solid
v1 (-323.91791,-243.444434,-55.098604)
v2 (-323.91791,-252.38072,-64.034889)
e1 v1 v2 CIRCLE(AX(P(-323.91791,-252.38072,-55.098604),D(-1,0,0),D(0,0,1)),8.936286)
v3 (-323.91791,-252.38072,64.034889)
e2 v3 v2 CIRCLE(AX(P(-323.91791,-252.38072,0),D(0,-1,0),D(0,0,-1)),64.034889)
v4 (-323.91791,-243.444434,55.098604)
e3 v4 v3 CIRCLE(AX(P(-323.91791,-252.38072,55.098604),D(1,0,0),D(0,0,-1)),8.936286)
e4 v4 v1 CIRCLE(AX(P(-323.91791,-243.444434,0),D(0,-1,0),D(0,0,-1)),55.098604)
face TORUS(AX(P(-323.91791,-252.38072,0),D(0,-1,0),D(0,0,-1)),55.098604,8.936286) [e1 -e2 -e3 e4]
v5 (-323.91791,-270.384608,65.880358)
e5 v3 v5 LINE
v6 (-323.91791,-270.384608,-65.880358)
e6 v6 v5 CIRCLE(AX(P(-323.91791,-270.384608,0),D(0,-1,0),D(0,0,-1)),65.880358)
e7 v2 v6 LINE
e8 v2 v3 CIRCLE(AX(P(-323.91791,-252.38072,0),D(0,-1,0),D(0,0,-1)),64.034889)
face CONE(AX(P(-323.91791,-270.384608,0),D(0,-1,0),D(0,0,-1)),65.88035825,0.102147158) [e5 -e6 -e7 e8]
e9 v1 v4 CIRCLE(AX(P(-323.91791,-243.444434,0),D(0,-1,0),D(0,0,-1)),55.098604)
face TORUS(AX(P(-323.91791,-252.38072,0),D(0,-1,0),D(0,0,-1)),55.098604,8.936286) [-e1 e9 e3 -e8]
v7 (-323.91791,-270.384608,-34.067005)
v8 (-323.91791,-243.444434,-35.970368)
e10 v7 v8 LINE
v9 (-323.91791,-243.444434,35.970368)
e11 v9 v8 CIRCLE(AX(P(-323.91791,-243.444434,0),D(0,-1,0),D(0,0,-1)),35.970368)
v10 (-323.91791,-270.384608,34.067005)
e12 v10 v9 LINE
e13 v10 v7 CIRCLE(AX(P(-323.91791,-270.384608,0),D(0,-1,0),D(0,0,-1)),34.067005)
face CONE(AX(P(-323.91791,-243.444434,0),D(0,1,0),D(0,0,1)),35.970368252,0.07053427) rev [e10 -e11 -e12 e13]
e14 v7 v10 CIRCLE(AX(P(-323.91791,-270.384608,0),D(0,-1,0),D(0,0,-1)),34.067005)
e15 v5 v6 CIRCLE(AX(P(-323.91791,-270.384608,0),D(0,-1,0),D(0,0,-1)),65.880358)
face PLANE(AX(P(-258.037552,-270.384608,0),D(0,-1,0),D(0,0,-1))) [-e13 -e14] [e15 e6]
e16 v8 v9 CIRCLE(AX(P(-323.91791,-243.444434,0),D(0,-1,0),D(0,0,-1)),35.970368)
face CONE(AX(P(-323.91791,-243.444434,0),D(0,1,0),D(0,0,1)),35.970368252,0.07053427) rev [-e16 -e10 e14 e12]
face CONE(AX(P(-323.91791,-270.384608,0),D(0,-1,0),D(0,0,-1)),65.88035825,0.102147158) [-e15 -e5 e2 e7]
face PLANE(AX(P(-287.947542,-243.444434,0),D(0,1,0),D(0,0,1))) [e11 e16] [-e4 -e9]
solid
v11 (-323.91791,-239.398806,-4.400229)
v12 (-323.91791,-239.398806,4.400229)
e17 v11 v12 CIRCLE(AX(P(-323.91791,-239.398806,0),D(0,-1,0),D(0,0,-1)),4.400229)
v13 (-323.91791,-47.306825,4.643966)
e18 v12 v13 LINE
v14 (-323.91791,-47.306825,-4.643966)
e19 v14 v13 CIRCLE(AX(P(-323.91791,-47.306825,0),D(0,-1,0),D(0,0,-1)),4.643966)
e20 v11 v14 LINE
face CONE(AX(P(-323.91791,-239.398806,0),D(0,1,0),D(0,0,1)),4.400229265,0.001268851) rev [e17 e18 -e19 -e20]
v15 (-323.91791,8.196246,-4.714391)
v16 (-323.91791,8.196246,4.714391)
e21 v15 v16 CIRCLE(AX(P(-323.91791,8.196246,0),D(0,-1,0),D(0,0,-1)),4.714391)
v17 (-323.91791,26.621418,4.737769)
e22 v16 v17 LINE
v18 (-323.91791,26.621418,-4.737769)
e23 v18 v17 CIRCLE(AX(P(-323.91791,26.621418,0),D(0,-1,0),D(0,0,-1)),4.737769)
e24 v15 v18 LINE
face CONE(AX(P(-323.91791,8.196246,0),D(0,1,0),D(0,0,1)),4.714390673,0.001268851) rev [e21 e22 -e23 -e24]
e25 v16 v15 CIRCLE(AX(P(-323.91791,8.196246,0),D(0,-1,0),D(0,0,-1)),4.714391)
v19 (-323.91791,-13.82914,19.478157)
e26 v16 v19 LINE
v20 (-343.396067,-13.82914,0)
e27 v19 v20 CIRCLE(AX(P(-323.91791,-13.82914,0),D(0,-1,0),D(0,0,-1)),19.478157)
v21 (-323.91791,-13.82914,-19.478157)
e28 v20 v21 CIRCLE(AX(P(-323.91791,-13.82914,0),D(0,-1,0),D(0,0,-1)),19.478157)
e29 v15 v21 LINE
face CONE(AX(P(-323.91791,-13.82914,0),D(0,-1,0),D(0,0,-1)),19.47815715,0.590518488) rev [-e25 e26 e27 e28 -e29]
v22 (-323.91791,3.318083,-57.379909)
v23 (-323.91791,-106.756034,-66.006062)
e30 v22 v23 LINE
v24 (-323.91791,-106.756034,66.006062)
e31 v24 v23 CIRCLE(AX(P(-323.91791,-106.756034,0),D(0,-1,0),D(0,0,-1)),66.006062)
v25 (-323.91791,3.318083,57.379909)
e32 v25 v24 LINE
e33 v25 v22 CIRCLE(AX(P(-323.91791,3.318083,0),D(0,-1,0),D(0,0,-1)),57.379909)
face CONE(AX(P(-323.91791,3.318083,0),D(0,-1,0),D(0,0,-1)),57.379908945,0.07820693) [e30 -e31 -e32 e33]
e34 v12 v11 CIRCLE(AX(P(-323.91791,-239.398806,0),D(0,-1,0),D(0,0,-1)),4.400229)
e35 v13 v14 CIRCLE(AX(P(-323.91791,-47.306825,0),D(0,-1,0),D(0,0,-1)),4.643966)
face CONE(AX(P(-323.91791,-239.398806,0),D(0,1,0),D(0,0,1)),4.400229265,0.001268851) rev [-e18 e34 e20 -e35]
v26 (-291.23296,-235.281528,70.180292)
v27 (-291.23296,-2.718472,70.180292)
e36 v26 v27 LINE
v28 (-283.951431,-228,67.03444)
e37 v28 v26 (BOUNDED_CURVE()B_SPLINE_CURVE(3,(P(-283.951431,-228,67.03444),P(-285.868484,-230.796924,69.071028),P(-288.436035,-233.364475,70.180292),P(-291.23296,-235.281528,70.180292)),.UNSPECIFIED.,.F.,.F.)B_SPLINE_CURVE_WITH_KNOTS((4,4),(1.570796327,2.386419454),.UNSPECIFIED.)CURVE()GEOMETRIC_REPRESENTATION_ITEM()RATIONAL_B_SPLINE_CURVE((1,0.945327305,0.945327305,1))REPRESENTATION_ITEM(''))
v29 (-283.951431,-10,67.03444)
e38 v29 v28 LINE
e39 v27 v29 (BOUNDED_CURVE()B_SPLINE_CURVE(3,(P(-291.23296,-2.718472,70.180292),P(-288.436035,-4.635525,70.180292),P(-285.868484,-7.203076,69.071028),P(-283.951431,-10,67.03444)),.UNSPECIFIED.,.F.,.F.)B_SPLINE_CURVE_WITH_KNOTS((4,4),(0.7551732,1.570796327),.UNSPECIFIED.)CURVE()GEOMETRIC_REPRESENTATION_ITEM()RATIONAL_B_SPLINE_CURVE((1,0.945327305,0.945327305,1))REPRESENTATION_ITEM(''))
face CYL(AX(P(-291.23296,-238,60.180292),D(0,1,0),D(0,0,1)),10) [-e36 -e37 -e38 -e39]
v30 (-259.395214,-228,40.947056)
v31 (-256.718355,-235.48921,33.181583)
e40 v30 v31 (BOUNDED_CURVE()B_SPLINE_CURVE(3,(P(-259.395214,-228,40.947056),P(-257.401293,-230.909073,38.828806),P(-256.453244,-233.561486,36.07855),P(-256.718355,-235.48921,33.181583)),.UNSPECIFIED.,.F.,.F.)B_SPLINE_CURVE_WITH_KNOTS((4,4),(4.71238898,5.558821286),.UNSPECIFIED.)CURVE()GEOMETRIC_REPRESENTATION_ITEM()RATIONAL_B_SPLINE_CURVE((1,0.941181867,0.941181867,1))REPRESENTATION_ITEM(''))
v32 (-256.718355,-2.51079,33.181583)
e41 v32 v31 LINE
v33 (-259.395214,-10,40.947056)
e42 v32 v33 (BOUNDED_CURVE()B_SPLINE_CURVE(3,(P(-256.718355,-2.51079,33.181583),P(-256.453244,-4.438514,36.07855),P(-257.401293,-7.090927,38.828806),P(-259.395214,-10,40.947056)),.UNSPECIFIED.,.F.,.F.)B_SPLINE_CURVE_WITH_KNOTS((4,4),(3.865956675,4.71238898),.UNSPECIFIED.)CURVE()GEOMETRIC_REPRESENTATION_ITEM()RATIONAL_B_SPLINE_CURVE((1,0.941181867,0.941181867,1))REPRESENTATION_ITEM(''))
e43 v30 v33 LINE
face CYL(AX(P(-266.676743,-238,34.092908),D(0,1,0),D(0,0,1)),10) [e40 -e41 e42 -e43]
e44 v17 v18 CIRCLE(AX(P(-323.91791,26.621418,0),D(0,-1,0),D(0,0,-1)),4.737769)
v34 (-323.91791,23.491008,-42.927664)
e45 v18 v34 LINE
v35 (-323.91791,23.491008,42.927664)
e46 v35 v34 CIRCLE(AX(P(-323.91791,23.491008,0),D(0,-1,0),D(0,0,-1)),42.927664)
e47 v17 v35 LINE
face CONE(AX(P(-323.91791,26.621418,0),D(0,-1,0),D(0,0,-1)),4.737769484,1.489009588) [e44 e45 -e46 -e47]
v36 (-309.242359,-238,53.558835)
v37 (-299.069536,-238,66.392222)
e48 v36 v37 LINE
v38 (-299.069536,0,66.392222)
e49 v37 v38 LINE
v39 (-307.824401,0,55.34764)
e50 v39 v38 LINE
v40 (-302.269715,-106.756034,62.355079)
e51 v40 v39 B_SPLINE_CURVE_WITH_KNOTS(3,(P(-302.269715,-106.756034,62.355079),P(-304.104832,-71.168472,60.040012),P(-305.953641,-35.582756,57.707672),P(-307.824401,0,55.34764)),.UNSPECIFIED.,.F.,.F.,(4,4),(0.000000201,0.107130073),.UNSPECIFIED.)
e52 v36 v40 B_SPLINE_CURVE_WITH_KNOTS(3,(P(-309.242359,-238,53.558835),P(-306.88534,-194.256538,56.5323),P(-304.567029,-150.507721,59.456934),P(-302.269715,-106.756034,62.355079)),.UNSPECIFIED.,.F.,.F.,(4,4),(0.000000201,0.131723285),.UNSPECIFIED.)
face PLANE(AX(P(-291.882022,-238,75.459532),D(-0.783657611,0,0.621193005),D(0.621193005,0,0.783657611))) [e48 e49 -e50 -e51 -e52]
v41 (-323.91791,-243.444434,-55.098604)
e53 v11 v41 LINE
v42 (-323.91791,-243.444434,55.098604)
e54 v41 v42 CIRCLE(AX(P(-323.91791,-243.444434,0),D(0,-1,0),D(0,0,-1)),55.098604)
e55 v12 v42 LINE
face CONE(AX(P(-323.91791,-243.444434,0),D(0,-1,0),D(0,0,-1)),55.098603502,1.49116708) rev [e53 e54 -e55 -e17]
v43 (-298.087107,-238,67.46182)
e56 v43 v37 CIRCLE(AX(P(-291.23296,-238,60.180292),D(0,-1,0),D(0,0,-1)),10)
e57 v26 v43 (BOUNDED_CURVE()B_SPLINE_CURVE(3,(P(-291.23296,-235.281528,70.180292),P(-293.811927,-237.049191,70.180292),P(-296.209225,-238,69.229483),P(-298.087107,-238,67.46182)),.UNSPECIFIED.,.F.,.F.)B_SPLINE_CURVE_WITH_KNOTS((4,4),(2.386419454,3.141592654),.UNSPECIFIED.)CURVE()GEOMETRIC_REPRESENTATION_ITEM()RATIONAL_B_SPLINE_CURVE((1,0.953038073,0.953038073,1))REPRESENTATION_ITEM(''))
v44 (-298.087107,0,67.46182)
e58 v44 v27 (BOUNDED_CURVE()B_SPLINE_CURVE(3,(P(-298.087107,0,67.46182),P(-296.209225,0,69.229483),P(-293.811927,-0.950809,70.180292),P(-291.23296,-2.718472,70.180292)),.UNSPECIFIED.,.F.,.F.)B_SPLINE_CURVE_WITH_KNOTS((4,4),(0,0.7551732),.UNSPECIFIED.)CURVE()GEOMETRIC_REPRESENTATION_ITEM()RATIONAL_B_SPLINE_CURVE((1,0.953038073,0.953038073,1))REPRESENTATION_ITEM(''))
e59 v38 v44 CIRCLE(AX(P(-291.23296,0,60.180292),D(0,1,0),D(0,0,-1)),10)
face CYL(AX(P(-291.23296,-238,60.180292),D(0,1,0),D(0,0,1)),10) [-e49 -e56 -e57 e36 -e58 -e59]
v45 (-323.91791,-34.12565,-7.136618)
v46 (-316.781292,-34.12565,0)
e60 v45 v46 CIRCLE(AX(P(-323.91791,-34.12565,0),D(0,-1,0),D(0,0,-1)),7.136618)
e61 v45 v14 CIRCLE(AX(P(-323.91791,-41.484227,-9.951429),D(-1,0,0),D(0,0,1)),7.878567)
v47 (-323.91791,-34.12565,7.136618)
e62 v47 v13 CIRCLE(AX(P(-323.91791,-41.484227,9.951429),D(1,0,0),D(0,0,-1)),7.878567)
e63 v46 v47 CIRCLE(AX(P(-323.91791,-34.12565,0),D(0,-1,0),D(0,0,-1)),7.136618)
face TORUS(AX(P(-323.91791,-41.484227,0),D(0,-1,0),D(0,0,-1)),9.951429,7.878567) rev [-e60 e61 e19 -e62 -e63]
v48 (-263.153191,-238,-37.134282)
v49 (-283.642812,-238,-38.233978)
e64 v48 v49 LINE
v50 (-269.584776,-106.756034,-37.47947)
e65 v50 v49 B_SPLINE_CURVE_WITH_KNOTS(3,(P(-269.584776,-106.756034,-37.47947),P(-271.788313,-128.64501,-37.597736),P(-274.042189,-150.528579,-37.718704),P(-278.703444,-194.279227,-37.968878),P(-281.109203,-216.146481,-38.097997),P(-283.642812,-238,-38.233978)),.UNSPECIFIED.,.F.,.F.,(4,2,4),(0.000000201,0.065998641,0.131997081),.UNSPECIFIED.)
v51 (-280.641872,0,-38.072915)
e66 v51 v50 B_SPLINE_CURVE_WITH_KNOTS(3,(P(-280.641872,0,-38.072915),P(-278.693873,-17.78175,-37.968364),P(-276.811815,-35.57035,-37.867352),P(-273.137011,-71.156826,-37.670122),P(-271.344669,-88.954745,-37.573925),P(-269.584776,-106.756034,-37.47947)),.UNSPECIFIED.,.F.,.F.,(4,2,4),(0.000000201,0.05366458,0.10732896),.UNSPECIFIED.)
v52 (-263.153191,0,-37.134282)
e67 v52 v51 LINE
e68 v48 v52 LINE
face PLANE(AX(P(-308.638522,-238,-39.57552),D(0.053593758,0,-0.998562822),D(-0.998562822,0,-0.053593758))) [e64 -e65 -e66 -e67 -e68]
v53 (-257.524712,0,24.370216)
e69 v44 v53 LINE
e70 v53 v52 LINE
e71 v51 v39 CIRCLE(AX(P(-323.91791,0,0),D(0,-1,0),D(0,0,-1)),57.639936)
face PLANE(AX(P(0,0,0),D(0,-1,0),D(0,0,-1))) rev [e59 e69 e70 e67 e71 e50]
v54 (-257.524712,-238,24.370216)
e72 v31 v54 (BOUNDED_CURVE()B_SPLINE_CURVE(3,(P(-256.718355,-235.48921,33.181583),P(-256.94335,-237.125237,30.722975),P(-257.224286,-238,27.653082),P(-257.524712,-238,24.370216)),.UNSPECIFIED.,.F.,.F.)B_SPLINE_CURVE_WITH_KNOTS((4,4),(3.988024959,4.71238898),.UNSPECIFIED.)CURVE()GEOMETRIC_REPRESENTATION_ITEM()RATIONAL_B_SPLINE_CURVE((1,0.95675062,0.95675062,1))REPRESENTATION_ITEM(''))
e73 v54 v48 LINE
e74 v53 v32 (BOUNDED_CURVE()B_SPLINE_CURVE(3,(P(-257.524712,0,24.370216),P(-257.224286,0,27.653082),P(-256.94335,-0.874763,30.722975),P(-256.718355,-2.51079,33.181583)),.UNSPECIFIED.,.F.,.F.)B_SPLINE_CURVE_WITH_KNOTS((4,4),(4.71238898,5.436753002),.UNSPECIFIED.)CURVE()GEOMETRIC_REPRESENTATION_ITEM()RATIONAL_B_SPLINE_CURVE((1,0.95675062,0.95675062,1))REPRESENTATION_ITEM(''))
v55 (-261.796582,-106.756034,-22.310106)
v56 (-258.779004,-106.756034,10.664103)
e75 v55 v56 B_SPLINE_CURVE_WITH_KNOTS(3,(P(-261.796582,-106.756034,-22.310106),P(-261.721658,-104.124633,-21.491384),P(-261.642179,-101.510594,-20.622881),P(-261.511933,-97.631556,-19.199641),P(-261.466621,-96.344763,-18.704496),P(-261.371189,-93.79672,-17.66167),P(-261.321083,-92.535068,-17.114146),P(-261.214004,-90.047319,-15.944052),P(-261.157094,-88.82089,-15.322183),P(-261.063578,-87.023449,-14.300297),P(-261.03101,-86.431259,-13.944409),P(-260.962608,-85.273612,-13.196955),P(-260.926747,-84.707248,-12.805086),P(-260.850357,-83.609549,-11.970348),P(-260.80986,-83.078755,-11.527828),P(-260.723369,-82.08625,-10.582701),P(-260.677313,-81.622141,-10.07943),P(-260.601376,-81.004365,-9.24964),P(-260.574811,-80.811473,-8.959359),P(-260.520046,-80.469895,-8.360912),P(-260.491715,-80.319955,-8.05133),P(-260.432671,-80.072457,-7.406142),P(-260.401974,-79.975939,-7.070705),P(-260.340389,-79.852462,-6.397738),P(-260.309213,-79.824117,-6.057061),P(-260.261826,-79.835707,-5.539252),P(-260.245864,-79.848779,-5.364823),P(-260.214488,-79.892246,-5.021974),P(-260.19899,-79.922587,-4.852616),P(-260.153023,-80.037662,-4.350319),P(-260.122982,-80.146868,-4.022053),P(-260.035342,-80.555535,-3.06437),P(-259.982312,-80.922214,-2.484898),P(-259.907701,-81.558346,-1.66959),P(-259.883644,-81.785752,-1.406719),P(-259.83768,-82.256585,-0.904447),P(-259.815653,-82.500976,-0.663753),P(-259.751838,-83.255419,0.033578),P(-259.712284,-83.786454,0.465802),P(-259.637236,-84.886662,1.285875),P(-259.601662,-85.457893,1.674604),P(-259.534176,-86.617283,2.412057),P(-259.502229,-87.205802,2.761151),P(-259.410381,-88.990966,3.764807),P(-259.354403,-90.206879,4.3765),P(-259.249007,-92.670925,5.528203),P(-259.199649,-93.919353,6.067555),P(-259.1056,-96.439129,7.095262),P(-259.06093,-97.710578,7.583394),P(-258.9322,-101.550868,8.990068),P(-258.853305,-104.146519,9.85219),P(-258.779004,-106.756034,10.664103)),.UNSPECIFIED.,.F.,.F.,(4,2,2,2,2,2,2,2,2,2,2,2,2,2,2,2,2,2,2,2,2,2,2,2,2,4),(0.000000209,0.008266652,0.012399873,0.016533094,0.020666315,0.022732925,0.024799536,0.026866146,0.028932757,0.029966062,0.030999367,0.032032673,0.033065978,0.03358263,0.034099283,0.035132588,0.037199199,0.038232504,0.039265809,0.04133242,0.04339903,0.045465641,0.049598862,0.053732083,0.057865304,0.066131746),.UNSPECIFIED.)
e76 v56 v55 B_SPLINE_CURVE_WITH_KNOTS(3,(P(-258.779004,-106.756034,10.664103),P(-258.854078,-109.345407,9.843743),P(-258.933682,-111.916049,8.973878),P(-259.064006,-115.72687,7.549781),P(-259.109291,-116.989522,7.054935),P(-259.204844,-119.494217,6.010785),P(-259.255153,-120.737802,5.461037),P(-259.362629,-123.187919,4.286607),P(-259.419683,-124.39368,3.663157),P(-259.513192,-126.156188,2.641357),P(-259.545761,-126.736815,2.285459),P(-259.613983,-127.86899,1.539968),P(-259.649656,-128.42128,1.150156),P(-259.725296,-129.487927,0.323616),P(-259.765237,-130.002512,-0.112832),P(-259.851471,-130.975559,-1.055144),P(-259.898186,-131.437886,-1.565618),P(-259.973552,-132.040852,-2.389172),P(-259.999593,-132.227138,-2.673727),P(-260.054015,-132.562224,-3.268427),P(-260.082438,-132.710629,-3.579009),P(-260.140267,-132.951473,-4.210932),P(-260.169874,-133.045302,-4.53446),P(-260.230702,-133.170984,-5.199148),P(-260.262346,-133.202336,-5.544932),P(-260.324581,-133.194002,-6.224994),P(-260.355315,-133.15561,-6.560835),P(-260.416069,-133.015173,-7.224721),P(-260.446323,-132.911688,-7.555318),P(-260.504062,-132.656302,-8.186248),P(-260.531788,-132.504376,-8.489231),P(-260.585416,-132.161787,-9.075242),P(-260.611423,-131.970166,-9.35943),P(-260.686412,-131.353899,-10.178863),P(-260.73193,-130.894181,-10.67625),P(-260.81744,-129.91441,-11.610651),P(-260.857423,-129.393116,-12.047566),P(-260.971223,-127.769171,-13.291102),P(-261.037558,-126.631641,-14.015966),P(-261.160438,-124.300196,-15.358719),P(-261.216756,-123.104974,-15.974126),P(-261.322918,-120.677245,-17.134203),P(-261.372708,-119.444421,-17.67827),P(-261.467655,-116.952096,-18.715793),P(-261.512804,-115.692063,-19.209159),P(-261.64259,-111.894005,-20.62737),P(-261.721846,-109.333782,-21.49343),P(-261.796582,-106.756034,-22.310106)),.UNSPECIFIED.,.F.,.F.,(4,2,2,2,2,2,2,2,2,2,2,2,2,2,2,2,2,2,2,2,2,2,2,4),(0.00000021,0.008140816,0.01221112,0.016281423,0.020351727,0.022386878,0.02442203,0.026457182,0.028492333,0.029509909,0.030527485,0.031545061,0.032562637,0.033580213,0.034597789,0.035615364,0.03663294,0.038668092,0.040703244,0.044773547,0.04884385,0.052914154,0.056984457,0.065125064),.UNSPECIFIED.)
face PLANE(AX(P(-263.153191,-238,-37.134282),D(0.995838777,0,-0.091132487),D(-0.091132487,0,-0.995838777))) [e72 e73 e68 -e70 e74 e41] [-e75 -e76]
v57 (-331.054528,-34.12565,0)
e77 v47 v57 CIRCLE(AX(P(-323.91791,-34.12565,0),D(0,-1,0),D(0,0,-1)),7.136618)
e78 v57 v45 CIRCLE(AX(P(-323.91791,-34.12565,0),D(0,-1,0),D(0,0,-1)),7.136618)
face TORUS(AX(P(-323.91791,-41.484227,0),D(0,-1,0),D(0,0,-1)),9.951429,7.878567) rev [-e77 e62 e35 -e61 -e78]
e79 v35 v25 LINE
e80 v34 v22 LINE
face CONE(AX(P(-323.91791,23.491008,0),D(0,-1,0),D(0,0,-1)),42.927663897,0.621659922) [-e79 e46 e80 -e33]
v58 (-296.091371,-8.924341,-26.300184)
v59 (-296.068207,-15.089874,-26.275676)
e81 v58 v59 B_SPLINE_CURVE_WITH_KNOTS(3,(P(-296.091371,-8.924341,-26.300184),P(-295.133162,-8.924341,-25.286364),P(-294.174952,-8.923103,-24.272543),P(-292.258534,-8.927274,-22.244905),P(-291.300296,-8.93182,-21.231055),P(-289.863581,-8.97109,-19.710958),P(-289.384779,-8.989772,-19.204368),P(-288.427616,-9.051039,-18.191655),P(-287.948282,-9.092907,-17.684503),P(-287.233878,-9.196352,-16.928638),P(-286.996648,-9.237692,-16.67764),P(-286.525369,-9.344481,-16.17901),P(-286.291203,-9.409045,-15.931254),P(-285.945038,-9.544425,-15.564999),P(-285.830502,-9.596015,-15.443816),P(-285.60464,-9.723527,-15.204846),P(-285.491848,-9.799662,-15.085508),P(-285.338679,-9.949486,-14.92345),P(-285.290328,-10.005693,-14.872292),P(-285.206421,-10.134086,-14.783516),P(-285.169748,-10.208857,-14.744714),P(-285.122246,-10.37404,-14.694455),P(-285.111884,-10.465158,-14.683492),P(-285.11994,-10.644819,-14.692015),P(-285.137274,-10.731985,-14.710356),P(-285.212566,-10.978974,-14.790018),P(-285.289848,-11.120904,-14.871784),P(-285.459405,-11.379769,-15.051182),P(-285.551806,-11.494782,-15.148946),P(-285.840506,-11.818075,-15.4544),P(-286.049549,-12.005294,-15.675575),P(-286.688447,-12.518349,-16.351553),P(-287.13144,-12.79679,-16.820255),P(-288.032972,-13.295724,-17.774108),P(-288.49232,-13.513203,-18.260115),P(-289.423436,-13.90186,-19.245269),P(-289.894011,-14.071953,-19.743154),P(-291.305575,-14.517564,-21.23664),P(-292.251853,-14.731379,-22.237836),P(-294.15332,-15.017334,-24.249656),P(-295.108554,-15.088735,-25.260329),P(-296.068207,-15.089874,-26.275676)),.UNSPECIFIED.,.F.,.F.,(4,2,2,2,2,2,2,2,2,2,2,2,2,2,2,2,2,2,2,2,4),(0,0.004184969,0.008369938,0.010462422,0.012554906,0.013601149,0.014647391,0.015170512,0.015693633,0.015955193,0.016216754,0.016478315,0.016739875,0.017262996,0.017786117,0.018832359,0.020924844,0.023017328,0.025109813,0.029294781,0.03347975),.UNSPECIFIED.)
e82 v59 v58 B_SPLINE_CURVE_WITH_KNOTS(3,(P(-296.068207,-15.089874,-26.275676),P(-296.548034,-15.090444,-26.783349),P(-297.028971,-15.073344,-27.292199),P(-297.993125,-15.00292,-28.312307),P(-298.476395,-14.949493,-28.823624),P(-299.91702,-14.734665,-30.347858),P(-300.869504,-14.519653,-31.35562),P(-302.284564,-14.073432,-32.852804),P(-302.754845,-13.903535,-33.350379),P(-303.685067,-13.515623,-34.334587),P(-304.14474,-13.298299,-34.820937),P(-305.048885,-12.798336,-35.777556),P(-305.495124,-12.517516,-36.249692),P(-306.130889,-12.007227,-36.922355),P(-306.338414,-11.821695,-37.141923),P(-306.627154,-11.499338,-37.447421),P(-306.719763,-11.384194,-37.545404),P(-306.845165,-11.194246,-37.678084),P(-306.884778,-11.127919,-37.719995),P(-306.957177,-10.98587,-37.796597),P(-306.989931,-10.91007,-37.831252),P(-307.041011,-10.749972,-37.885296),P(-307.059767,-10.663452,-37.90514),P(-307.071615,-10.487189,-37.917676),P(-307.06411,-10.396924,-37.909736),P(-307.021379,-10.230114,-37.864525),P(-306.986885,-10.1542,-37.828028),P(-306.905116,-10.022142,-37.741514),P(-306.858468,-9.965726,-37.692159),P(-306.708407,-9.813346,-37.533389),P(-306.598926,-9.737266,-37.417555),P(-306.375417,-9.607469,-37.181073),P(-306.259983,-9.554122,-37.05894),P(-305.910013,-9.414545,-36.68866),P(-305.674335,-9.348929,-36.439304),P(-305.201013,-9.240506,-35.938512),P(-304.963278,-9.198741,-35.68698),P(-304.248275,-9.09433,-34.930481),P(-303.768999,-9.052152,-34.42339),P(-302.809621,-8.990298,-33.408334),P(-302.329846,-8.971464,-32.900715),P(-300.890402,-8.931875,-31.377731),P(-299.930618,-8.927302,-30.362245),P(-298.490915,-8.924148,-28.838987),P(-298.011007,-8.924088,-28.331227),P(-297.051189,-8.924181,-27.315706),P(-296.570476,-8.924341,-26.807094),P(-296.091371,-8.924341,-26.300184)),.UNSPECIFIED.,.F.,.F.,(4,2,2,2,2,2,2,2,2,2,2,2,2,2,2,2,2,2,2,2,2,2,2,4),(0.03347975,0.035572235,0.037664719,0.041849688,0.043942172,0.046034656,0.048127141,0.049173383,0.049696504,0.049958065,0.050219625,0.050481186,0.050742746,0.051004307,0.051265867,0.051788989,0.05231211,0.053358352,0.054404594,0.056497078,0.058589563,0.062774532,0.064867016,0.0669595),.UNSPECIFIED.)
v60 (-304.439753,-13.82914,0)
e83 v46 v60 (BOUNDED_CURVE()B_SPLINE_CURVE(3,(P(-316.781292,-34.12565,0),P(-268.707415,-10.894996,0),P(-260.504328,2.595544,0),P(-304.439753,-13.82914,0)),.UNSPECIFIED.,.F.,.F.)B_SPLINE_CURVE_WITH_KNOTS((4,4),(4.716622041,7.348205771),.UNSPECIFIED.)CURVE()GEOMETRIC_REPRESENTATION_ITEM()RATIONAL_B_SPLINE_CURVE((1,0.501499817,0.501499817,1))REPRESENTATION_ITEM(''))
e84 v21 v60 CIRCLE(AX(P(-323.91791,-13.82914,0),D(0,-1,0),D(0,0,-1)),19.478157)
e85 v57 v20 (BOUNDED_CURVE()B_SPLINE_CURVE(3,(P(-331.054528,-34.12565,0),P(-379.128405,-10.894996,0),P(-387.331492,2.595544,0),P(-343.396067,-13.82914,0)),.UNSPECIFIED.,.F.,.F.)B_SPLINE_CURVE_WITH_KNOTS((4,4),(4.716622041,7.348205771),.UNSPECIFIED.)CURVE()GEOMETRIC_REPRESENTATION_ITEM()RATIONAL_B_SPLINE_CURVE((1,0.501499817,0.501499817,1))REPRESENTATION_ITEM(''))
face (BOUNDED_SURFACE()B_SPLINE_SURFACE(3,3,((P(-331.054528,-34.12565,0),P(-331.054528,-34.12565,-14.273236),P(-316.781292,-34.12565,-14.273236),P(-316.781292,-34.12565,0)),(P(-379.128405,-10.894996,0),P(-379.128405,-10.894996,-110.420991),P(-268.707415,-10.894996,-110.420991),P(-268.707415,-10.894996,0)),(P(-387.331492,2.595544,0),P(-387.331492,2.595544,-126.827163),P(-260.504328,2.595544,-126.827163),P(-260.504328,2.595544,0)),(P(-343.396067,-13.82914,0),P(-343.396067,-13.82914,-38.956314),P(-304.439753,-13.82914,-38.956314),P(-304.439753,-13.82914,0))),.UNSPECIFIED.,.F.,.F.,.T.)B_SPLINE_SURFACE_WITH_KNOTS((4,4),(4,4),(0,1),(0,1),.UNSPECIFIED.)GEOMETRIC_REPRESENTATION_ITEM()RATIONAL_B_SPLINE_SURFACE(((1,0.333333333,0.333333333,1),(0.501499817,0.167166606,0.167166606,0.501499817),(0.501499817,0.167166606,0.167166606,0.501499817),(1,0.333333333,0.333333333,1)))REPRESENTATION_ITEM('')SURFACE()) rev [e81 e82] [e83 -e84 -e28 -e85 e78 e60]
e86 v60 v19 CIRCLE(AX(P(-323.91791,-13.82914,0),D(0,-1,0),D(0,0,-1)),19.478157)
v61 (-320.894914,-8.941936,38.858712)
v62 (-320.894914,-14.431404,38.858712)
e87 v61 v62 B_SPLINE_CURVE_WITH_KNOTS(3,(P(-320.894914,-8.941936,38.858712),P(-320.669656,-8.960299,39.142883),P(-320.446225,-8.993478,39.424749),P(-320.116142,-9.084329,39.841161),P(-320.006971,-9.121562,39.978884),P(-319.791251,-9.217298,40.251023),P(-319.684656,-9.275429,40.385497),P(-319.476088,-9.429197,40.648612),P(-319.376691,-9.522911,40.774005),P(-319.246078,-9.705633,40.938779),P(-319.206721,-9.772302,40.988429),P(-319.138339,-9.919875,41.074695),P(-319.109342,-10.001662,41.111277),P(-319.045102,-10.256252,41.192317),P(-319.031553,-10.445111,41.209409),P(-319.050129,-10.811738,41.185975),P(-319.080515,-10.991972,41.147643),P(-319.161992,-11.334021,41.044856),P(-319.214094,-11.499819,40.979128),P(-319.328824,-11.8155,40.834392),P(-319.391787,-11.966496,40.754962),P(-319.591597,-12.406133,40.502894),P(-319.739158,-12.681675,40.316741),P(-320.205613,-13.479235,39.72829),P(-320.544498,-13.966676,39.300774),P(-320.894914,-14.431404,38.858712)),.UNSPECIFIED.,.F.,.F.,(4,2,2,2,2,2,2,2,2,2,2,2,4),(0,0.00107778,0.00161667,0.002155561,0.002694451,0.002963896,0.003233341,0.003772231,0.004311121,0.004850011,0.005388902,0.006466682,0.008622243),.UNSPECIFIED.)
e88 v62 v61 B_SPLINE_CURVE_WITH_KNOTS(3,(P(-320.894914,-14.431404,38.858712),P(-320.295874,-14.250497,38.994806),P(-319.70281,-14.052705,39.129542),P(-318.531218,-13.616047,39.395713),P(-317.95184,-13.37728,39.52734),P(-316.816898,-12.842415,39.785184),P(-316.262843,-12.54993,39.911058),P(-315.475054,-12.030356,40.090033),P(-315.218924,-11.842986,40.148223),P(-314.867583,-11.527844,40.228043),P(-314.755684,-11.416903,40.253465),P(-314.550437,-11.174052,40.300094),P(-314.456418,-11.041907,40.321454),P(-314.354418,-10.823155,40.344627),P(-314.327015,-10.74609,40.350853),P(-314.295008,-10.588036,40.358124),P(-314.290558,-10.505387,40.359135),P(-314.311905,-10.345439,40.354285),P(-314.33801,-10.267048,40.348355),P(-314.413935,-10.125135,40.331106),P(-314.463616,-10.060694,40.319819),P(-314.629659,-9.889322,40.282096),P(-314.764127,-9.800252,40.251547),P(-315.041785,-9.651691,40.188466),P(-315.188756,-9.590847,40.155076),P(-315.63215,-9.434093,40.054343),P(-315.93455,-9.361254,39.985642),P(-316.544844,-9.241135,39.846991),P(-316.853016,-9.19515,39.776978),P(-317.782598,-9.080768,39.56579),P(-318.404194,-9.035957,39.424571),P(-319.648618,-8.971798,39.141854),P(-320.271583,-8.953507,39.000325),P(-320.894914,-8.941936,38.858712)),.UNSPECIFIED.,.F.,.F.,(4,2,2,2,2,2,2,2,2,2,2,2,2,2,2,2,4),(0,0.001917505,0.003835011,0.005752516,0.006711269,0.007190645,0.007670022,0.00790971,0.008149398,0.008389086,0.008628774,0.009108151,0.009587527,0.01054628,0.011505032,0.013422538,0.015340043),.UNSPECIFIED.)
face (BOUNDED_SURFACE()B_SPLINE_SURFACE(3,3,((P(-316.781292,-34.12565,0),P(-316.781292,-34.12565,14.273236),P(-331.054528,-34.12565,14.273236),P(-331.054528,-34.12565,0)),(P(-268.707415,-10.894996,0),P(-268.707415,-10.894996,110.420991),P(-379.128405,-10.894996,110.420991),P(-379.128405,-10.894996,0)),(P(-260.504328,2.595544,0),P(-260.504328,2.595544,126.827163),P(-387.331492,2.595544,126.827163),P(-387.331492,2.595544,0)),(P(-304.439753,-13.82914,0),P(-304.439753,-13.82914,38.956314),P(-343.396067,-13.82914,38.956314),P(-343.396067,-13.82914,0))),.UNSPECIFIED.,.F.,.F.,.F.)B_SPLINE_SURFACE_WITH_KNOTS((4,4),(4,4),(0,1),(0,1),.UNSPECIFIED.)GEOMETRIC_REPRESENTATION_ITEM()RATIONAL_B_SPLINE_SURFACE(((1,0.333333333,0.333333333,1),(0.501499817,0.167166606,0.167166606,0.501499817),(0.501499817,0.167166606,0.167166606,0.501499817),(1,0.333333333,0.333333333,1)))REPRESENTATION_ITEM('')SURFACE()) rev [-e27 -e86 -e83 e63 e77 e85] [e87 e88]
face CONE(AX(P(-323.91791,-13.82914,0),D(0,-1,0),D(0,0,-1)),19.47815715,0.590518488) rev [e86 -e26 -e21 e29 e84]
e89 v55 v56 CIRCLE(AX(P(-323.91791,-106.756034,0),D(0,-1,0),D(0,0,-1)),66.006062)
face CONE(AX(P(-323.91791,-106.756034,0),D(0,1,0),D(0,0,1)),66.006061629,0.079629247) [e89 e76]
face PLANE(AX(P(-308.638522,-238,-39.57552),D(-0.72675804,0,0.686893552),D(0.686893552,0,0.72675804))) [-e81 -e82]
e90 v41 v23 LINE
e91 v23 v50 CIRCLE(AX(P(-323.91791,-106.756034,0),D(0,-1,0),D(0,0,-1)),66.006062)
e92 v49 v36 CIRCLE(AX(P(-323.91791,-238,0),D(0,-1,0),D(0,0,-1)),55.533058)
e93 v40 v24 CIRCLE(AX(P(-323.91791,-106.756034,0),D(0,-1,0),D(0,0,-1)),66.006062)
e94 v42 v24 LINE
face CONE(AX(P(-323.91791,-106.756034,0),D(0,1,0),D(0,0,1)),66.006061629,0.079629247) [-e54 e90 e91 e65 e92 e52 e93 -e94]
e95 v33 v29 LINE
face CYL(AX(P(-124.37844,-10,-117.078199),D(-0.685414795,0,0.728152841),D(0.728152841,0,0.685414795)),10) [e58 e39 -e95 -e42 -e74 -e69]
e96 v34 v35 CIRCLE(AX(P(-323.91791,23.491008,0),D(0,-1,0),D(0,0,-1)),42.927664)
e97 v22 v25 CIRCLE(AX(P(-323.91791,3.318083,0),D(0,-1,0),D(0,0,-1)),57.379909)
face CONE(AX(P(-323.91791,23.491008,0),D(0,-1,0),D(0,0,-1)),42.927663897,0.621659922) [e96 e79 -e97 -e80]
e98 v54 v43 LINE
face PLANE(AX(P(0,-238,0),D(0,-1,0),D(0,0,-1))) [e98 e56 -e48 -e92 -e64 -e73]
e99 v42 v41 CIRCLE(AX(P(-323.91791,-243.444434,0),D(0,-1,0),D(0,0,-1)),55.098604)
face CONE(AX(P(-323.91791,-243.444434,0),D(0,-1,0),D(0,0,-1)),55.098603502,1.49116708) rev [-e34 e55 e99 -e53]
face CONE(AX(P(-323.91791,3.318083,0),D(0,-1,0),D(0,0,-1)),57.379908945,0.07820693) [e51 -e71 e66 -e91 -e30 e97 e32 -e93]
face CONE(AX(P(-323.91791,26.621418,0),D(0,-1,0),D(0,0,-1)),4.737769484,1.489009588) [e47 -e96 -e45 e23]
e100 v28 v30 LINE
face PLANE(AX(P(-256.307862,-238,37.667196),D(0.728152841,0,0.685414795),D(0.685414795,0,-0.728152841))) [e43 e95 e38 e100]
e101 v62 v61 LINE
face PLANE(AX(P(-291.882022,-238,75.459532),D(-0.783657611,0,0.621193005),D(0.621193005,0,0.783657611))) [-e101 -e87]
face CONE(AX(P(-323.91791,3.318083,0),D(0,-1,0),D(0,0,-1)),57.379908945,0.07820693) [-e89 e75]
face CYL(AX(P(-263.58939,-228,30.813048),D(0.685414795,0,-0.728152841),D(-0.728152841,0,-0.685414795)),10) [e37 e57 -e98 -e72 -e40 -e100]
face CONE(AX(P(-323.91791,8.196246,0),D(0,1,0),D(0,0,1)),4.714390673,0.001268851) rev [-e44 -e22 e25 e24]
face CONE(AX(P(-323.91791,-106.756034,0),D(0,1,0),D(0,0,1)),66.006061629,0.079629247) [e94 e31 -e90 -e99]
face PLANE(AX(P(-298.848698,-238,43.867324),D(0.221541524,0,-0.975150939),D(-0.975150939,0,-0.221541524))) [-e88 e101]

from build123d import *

# Parameters (mm, degrees)
BOSS_EXTRUDE1_DEPTH = 238
FILLET1_R           = 10


with BuildPart() as part:
    # Sketch2 → Revolve1 (revolve)
    with BuildSketch(Plane.XY, mode=Mode.PRIVATE) as revolve1_sk:
        with BuildLine():
            Line((-328.655679382, 26.621417908), (-366.845573795, 23.491008025))
            Line((-366.845573795, 23.491008025), (-381.297818843, 3.318082644))
            Line((-381.297818843, 3.318082644), (-389.923971527, -106.756034051))
            Line((-389.923971527, -106.756034051), (-379.0165134, -243.444434045))
            Line((-379.0165134, -243.444434045), (-328.318139163, -239.398806221))
            Line((-328.318139163, -239.398806221), (-328.561875404, -47.306824662))
            ThreePointArc((-328.561875404, -47.306824662), (-341.610700787, -42.948172925), (-331.054528121, -34.125650186))
            add(Edge.make_bspline(
                [(-343.396067048, -13.829139561), (-369.788894566, -3.962526401), (-364.86114786, -12.066545193), (-359.933401153, -20.170563985), (-331.054528121, -34.125650186)],
                knots=[2.07657219, 2.07657219, 2.07657219, 3.392364055, 3.392364055, 4.70815592, 4.70815592, 4.70815592], degree=2, weights=[1, 0.791280521, 1, 0.791280521, 1]))
            Line((-343.396067048, -13.829139561), (-328.632300571, 8.196246))
            Line((-328.632300571, 8.196246), (-328.655679382, 26.621417908))
        make_face()
    revolve(revolve1_sk.sketch.rotate(Axis((-323.917909898, -239.047676817, 0), (0, 1, 0)), 270), axis=Axis((-323.917909898, -239.047676817, 0), (0, 1, 0)))

    # Sketch3 → Boss-Extrude1 (add)
    with BuildSketch(Plane(origin=(0, 0, 0), x_dir=(1, 0, 0), z_dir=(0, 1, 0))):
        Polygon((-308.638521792, 39.575519818), (-263.153191414, 37.134281554), (-256.30786178, -37.667195745), (-291.882022487, -75.459531675), (-320.894913791, -38.858712112), (-298.848697668, -43.867323718), (-278.655979488, -19.734201659), (-273.594686567, 2.497883967), align=None)
    extrude(amount=-BOSS_EXTRUDE1_DEPTH)

    # Fillet1
    fillet1_edges = [part.edges().sort_by_distance(p)[0] for p in [
        (-291.882022487, -119, 75.459531675),
        (-274.094942134, -238, 56.56336371),
        (-256.30786178, -119, 37.667195745),
        (-274.094942134, 0, 56.56336371),
    ]]
    fillet(fillet1_edges, radius=FILLET1_R)


with BuildPart() as body_2:
    # Sketch5 → Revolve2 (revolve)
    with BuildSketch(Plane.XY, mode=Mode.PRIVATE) as revolve2_sk:
        with BuildLine():
            Line((-287.947541646, -243.444434045), (-268.819306396, -243.444434045))
            ThreePointArc((-268.819306396, -243.444434045), (-262.500398164, -246.061811534), (-259.883020675, -252.380719766))
            Line((-259.883020675, -252.380719766), (-258.037551648, -270.384607737))
            Line((-258.037551648, -270.384607737), (-289.850904646, -270.384607737))
            Line((-289.850904646, -270.384607737), (-287.947541646, -243.444434045))
        make_face()
    revolve(revolve2_sk.sketch.rotate(Axis((-323.917909898, 26.621417908, 0), (0, 1, 0)), 90), axis=Axis((-323.917909898, 26.621417908, 0), (0, 1, 0)))


solid = Compound([part.part, body_2.part])
